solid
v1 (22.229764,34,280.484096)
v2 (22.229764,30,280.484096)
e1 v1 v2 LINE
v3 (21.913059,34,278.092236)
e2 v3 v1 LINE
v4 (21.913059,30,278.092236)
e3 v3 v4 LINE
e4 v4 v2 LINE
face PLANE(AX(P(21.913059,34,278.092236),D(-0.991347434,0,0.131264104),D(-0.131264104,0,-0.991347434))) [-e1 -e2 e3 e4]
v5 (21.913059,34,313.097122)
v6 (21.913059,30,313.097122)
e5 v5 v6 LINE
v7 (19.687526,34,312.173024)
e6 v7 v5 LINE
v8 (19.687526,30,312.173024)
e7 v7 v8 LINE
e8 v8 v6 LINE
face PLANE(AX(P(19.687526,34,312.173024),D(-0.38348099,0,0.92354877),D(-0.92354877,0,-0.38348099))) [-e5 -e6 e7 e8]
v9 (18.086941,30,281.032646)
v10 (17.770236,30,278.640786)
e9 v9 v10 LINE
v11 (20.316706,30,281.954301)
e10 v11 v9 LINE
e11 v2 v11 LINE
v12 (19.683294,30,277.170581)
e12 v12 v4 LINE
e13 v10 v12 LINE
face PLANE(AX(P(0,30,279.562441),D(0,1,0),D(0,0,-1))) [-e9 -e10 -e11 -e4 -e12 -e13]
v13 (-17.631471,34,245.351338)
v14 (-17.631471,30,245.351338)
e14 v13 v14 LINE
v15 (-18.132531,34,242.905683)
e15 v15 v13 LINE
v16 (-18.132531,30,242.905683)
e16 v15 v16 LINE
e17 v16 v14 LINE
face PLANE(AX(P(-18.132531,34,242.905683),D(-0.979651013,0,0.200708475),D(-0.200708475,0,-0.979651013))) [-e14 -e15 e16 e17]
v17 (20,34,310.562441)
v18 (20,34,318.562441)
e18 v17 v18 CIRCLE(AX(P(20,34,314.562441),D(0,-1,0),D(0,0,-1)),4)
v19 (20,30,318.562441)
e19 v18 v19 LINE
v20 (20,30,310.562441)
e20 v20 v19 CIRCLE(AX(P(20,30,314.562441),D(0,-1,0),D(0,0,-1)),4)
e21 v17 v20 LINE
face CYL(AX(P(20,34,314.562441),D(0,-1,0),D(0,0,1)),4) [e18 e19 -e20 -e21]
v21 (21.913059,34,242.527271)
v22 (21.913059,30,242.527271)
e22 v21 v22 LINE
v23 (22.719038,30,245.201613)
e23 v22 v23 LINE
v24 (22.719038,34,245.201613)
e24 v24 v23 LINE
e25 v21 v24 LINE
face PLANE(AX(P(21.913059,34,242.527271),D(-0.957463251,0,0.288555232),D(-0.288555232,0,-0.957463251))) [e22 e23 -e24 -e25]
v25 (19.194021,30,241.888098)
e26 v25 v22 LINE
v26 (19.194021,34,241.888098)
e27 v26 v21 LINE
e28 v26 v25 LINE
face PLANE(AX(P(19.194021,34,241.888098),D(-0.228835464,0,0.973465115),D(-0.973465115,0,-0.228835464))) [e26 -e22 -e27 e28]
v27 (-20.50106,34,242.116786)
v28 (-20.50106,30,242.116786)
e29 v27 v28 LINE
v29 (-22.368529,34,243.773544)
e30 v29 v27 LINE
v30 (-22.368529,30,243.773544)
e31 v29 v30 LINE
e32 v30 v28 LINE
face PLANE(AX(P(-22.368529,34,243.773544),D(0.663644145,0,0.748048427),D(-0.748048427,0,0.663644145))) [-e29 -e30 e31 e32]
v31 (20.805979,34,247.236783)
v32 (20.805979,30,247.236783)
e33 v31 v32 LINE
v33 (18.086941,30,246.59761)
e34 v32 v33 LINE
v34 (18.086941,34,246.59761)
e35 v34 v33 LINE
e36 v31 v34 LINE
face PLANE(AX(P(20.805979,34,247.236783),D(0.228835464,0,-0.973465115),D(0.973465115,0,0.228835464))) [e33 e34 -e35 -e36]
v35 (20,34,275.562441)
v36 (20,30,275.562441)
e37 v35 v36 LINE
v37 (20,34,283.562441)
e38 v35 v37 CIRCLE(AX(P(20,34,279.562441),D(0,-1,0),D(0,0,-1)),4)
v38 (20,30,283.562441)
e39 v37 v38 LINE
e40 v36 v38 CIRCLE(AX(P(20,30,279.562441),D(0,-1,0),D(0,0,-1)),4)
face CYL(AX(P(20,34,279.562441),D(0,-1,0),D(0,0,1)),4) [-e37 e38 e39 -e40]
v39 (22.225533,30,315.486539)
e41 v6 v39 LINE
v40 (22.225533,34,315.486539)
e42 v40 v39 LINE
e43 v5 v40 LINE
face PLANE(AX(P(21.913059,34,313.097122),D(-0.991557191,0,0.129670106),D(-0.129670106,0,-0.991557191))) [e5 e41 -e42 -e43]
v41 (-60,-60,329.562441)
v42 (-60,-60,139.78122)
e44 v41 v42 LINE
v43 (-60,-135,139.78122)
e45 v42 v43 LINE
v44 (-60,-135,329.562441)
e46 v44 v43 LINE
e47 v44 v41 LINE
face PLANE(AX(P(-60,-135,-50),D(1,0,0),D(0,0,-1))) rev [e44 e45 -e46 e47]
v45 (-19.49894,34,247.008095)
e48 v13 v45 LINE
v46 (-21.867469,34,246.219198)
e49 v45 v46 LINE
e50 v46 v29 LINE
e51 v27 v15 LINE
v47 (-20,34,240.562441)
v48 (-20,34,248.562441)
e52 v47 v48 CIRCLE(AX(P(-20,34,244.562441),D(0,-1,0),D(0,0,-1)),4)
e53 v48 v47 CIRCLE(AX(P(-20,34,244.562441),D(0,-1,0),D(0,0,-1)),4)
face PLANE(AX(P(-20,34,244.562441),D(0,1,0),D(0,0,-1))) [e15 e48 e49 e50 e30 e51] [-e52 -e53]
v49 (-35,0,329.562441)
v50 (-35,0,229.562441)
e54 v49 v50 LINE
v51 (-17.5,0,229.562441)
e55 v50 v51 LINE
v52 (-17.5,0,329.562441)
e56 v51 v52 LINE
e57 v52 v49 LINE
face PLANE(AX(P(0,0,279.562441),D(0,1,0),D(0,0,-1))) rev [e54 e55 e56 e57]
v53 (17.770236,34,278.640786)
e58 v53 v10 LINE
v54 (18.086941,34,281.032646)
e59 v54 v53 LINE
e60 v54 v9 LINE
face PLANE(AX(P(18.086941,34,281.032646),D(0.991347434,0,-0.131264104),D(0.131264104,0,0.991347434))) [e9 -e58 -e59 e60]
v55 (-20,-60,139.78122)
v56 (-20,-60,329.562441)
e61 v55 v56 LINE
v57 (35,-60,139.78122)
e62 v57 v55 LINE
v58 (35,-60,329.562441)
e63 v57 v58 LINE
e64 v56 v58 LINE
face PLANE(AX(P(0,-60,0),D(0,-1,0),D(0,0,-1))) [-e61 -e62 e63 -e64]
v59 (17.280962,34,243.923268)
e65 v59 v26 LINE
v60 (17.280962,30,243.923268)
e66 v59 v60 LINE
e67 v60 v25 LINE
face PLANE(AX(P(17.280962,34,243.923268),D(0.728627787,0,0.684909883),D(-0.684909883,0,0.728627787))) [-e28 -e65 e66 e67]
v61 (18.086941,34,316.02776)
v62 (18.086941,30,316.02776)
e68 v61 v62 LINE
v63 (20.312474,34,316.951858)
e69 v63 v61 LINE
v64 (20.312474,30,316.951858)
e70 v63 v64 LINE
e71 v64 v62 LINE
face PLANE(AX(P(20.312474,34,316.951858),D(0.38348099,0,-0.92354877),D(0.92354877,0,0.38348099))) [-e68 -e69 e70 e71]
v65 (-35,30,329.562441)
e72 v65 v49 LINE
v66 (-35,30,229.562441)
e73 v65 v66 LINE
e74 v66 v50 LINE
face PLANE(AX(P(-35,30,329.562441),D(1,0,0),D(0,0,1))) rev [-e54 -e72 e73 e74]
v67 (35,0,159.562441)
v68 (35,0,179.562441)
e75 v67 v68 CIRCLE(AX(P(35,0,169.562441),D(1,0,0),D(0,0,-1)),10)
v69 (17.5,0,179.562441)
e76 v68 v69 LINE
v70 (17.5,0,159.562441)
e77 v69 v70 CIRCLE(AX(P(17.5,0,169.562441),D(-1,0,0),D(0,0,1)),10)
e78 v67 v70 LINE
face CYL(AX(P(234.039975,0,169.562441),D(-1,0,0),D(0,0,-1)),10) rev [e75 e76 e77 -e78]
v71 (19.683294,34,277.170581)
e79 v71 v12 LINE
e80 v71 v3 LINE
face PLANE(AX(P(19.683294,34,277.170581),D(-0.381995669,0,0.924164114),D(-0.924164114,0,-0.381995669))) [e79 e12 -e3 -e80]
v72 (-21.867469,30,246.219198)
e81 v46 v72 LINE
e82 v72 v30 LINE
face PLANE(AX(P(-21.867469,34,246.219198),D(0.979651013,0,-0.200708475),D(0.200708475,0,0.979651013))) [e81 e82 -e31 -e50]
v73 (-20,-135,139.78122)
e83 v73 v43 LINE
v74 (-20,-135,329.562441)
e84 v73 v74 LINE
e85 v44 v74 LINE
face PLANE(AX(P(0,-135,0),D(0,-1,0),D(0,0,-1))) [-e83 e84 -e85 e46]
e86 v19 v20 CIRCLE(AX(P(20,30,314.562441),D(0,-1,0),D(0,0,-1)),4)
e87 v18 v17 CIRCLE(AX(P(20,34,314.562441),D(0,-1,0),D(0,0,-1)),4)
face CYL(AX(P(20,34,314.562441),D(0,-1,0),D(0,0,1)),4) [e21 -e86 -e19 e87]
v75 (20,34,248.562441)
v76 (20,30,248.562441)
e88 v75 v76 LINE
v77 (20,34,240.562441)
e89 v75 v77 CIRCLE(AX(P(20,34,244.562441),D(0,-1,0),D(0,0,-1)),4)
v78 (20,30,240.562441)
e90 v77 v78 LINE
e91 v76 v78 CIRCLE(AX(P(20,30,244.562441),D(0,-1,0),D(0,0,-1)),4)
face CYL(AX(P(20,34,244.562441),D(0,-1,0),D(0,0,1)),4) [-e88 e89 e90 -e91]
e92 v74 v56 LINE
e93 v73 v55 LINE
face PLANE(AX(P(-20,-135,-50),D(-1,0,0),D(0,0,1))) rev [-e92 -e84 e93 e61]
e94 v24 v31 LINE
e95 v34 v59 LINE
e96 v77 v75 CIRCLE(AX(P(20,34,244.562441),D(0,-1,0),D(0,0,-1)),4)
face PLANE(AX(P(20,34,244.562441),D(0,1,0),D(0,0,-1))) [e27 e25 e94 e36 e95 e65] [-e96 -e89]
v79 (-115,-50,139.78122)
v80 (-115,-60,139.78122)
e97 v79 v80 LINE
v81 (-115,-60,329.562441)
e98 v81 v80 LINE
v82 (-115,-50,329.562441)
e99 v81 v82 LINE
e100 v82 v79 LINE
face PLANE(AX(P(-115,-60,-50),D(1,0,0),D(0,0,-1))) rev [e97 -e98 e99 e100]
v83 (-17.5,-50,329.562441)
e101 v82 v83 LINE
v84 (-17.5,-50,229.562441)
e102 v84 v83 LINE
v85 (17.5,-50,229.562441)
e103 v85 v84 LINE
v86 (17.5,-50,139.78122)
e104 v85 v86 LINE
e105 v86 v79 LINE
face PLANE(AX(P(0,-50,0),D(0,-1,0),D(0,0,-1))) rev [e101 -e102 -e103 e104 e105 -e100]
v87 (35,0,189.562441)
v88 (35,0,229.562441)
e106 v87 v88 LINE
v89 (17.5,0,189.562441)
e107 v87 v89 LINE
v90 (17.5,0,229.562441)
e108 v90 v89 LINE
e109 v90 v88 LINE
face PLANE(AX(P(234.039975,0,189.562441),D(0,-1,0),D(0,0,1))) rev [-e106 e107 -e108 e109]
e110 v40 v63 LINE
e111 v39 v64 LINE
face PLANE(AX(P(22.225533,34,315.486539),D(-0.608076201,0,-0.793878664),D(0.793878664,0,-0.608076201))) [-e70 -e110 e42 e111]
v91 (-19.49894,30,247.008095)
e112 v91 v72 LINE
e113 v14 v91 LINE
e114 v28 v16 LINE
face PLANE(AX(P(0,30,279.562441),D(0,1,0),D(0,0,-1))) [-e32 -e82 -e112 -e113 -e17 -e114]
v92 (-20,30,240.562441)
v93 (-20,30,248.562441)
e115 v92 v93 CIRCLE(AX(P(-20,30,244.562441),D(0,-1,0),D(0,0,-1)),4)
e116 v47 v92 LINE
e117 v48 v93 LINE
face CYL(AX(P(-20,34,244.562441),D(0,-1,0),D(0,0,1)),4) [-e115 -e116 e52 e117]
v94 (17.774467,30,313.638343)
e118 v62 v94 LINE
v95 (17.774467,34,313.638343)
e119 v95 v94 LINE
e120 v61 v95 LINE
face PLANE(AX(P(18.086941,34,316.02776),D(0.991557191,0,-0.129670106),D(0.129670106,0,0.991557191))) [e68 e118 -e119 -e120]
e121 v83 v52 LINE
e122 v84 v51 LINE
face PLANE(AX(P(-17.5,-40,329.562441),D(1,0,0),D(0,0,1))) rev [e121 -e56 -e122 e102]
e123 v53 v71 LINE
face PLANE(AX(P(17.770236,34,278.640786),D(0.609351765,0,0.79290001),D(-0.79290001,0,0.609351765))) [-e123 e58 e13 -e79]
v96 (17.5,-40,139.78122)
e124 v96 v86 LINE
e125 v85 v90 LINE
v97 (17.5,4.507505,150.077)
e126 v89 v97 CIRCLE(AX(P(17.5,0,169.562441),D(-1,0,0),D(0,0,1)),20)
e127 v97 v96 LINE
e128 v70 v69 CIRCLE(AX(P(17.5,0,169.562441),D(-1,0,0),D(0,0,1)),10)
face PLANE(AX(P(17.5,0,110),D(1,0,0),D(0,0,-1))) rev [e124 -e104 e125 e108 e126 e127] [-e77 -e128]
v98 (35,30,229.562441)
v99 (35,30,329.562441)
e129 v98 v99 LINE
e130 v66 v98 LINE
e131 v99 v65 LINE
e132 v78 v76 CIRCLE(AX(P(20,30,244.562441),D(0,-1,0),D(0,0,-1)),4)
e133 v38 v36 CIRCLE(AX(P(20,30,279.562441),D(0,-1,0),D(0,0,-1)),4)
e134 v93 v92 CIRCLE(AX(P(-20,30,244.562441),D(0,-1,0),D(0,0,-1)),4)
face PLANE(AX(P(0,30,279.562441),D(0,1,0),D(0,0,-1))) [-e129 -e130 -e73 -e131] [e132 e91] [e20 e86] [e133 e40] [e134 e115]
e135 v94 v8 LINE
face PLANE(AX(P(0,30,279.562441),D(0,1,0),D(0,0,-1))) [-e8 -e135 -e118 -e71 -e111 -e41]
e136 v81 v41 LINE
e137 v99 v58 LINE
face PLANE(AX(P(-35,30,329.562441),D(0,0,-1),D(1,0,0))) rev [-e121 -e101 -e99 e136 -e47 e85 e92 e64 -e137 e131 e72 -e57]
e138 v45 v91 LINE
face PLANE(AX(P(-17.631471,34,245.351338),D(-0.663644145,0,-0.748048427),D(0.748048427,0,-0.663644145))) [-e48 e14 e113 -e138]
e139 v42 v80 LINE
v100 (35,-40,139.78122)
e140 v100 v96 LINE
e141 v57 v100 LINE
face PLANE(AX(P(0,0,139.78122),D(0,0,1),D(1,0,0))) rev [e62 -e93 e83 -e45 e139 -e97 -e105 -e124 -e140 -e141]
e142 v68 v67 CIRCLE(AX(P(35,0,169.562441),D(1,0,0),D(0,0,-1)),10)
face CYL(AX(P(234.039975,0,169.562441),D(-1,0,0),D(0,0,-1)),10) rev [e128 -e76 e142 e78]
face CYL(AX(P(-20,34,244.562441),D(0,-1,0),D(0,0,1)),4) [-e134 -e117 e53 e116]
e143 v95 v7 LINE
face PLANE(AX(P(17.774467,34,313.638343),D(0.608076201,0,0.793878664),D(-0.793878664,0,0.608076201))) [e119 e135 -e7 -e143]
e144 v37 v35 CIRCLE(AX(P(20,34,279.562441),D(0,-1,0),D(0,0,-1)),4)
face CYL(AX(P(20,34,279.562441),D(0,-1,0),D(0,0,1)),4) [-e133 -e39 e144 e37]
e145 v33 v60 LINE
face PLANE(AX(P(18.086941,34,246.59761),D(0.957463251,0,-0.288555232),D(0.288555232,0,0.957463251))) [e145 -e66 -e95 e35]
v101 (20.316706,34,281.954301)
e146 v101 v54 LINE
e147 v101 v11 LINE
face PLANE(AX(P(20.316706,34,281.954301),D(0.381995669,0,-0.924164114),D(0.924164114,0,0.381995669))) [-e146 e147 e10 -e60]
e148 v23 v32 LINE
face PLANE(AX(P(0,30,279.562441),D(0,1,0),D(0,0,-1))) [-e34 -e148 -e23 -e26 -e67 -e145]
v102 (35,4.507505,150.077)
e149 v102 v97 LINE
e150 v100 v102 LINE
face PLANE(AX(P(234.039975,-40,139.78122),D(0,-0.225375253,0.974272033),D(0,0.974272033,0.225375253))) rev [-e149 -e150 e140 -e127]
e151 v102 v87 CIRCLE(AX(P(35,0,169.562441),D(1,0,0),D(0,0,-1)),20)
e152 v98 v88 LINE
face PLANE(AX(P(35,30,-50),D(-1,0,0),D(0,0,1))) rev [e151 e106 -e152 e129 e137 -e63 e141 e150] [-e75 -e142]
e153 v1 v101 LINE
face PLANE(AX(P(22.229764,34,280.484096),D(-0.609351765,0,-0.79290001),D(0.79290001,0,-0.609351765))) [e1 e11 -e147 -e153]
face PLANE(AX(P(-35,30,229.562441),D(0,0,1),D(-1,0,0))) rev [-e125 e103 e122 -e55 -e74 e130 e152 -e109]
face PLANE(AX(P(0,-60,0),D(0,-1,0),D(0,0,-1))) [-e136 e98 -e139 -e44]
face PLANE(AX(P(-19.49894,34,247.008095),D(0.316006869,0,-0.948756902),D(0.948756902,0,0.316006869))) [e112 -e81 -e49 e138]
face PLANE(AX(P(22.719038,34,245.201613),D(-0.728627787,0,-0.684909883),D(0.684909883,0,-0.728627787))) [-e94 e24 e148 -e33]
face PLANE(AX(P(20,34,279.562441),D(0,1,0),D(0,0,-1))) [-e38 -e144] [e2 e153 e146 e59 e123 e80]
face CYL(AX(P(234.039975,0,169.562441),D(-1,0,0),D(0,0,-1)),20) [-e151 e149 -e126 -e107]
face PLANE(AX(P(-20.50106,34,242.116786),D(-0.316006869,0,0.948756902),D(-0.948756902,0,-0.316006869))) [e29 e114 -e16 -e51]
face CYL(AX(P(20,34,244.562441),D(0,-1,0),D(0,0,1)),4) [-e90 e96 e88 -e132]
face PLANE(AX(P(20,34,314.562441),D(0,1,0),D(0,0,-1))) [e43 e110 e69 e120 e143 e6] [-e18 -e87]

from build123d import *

# Parameters (mm, degrees)
SKETCH1_W           = 70
SKETCH1_H           = 100
BOSS_EXTRUDE1_DEPTH = 30
SKETCH2_R           = 4
BOSS_EXTRUDE2_DEPTH = 4
SKETCH3_W           = 35
SKETCH3_H           = 100
BOSS_EXTRUDE3_DEPTH = 40
SKETCH4_R           = 10
BOSS_EXTRUDE4_DEPTH = 17.5
BOSS_EXTRUDE5_DEPTH = 10
SKETCH6_W           = 150
SKETCH6_H           = 189.781220368
BOSS_EXTRUDE6_DEPTH = 10
SKETCH7_W           = 40
SKETCH7_H           = 189.781220368
BOSS_EXTRUDE7_DEPTH = 75
SKETCH8_W           = 213.425004002
SKETCH8_H           = 201.568059336
CUT_EXTRUDE1_DEPTH  = 210


with BuildPart() as part:
    # Sketch1 → Boss-Extrude1 (new body)
    with BuildSketch(Plane(origin=(0, 0, 0), x_dir=(1, 0, 0), z_dir=(0, 1, 0))):
        Rectangle(SKETCH1_W, SKETCH1_H)
    extrude(amount=BOSS_EXTRUDE1_DEPTH)

    # Sketch2 → Boss-Extrude2 (add)
    # profile 1 of 4: a face of its own
    with BuildSketch(Plane(origin=(0, 30, 0), x_dir=(1, 0, 0), z_dir=(0, 1, 0))):
        with Locations(Location((-20, -35, 0), (0, 0, 270))):
            Circle(SKETCH2_R)
        Polygon((-18.132531053, -36.656757487), (-17.631471454, -34.211103194), (-19.498940402, -32.554345707), (-21.867468947, -33.343242513), (-22.368528546, -35.788896806), (-20.501059598, -37.445654293), align=None, mode=Mode.SUBTRACT)
    # profile 2 of 4: a face of its own
    with BuildSketch(Plane(origin=(0, 30, 0), x_dir=(1, 0, 0), z_dir=(0, 1, 0))):
        with Locations(Location((20, -35, 0), (0, 0, 270))):
            Circle(SKETCH2_R)
        Polygon((21.913058762, -37.035169602), (22.719037957, -34.360827314), (20.805979195, -32.325657712), (18.086941238, -32.964830398), (17.280962043, -35.639172686), (19.194020805, -37.674342288), align=None, mode=Mode.SUBTRACT)
    # profile 3 of 4: a face of its own
    with BuildSketch(Plane(origin=(0, 30, 0), x_dir=(1, 0, 0), z_dir=(0, 1, 0))):
        with Locations(Location((20, 0, 0), (0, 0, 270))):
            Circle(SKETCH2_R)
        Polygon((21.913058762, -1.47020522), (22.229764451, 0.921654877), (20.316705689, 2.391860097), (18.086941238, 1.47020522), (17.770235549, -0.921654877), (19.683294311, -2.391860097), align=None, mode=Mode.SUBTRACT)
    # profile 4 of 4: a face of its own
    with BuildSketch(Plane(origin=(0, 30, 0), x_dir=(1, 0, 0), z_dir=(0, 1, 0))):
        with Locations(Location((20, 35, 0), (0, 0, 270))):
            Circle(SKETCH2_R)
        Polygon((21.913058762, 33.534680981), (22.225532876, 35.924097978), (20.312474114, 37.389416996), (18.086941238, 36.465319019), (17.774467124, 34.075902022), (19.687525886, 32.610583004), align=None, mode=Mode.SUBTRACT)
    extrude(amount=BOSS_EXTRUDE2_DEPTH)

    # Sketch3 → Boss-Extrude3 (add)
    with BuildSketch(Plane.XZ):
        Rectangle(SKETCH3_W, SKETCH3_H)
    extrude(amount=BOSS_EXTRUDE3_DEPTH)

    # Sketch4 → Boss-Extrude4 (add)
    with BuildSketch(Plane(origin=(17.5, 0, 0), x_dir=(0, 0, -1), z_dir=(1, 0, 0))):
        with BuildLine():
            Line((-50, -40), (-139.781220368, -40))
            Line((-139.781220368, -40), (-129.48544067, 4.507505064))
            ThreePointArc((-129.48544067, 4.507505064), (-107.731609976, 19.87094378), (-90, 0))
            Line((-90, 0), (-50, 0))
            Line((-50, 0), (50, 0))
            Line((50, 0), (50, -40))
            Line((50, -40), (-50, -40))
        make_face()
        with Locations(Location((-110, 0, 0), (0, 0, 180))):
            Circle(SKETCH4_R, mode=Mode.SUBTRACT)
    extrude(amount=BOSS_EXTRUDE4_DEPTH)

    # Sketch5 → Boss-Extrude5 (add)
    with BuildSketch(Plane.XZ.offset(40)):
        Polygon((17.5, 139.781220368), (35, 139.781220368), (35, -50), (-17.5, -50), (-17.5, 50), (17.5, 50), align=None)
    extrude(amount=BOSS_EXTRUDE5_DEPTH)

    # Sketch6 → Boss-Extrude6 (add)
    with BuildSketch(Plane.XZ.offset(50)):
        with Locations((-40, 44.890610184)):
            Rectangle(SKETCH6_W, SKETCH6_H)
    extrude(amount=BOSS_EXTRUDE6_DEPTH)

    # Sketch7 → Boss-Extrude7 (add)
    with BuildSketch(Plane.XZ.offset(60)):
        with Locations((-40, 44.890610184)):
            Rectangle(SKETCH7_W, SKETCH7_H)
    extrude(amount=BOSS_EXTRUDE7_DEPTH)

    # Mirror3: part across plane


with BuildPart() as part_1:
    add(part.part)
    add(part.part.mirror(Plane(origin=(17.5, -50, 139.781220368), x_dir=(1, 0, 0), z_dir=(0, 0, -1))))

    # Sketch8 → Cut-Extrude1 (cut)
    with BuildSketch(Plane.XY.offset(139.781220368)):
        with Locations((-37.145550358, -46.351954617)):
            Rectangle(SKETCH8_W, SKETCH8_H)
    extrude(amount=-CUT_EXTRUDE1_DEPTH, mode=Mode.SUBTRACT)


solid = part_1.part
